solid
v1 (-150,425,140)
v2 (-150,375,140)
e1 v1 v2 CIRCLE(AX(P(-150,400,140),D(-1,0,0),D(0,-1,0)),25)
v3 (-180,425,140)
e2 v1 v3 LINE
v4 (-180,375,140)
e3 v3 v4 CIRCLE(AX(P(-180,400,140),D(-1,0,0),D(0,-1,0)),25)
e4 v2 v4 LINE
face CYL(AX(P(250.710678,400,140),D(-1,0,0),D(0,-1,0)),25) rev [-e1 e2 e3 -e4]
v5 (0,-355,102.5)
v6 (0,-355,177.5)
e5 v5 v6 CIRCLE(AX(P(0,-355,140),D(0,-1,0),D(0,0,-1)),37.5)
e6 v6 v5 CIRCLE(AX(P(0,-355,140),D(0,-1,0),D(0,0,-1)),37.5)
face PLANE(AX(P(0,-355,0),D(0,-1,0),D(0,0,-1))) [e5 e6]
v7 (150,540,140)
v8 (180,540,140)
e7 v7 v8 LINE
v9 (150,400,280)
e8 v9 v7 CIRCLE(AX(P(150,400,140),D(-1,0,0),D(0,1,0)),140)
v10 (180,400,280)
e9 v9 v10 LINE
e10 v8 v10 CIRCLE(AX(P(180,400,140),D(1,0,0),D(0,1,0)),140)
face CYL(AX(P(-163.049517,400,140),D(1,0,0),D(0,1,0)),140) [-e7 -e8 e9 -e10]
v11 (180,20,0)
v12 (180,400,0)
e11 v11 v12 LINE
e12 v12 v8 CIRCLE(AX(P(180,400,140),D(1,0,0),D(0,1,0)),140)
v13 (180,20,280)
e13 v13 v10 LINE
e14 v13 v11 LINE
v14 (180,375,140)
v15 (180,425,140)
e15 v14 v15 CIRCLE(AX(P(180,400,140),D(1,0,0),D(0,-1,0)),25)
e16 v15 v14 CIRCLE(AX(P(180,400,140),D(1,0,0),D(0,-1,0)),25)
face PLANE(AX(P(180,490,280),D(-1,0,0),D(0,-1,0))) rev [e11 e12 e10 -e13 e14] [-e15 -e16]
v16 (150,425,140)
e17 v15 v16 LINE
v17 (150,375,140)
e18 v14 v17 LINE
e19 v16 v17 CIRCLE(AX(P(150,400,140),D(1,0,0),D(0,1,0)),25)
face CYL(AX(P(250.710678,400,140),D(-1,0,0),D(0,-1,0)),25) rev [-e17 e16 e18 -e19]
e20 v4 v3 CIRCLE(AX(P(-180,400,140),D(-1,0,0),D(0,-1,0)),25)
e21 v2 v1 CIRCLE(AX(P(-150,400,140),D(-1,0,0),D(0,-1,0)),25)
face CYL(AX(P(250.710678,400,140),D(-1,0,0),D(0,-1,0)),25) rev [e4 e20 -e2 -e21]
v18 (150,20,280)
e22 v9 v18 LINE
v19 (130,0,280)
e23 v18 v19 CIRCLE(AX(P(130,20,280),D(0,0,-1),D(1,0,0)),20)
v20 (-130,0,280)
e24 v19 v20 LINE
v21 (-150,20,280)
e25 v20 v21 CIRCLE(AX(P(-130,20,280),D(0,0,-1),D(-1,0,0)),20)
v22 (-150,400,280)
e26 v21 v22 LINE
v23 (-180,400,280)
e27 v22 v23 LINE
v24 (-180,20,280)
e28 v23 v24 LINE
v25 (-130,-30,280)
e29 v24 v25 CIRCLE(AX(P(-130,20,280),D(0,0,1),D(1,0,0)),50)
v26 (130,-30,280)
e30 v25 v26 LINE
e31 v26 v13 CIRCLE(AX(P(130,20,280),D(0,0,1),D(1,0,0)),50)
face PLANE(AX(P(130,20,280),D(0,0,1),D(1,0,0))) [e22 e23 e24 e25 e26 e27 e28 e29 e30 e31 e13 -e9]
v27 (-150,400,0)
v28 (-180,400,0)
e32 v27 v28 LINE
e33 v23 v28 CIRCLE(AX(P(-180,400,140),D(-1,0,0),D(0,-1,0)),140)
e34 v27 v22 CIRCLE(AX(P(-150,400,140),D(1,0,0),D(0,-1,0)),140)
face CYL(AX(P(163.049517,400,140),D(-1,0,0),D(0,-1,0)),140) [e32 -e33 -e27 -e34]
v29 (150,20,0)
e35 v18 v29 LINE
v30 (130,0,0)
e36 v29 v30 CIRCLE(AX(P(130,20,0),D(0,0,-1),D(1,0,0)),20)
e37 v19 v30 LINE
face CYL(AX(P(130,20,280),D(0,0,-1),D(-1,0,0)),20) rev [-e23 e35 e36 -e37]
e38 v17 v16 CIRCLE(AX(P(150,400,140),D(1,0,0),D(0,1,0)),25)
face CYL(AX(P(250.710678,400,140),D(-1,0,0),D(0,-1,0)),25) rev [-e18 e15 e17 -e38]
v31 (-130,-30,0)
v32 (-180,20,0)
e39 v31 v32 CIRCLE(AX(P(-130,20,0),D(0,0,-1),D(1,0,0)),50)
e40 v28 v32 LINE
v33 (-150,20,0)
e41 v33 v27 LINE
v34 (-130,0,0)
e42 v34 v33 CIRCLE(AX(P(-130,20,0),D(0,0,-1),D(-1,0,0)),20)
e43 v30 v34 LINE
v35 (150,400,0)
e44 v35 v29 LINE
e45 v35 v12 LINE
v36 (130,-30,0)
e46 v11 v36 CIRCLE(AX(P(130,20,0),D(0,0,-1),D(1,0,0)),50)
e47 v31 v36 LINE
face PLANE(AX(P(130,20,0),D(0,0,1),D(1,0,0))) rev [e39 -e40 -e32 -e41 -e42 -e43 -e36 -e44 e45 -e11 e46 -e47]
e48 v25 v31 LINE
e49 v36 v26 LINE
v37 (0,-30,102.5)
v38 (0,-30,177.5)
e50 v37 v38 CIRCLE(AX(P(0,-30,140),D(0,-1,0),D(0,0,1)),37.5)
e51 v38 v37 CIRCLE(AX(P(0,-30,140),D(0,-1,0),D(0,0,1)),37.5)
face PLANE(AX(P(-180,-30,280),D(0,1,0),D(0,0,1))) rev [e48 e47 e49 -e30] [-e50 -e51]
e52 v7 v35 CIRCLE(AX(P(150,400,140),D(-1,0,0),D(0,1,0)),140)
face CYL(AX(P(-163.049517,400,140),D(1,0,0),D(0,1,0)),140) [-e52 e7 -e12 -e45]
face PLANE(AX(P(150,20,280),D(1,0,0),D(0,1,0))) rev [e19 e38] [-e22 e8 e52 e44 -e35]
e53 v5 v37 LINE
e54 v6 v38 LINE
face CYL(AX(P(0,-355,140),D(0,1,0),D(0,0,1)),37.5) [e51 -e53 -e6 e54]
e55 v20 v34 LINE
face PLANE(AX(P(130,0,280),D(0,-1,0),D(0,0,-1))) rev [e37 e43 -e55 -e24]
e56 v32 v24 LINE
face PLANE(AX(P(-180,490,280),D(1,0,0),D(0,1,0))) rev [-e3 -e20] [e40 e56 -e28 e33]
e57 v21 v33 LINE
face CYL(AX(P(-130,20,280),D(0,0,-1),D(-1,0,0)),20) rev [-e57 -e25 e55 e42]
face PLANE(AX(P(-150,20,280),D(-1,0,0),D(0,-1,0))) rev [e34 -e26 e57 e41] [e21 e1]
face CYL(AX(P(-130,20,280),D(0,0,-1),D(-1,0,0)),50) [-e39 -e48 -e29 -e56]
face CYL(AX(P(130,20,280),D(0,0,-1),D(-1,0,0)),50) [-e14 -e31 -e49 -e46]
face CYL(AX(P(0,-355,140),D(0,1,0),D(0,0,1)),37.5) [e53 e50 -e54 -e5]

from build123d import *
from build123d.topology import SkipClean

# Parameters (mm, degrees)
BOSS_EXTRUDE1_DEPTH = 280
FILLET1_R           = 50
BOSS_EXTRUDE3_START = -30
BOSS_EXTRUDE3_DEPTH = 30
CUT_EXTRUDE5_START  = -30
CUT_EXTRUDE5_DEPTH  = 30
BOSS_EXTRUDE4_DEPTH = 30
CUT_EXTRUDE6_DEPTH  = 30
BOSS_EXTRUDE5_DEPTH = 325
CUT_EXTRUDE7_REACH  = 708.824
SKETCH7_R           = 25


with BuildPart() as part:
    # Sketch1 → Boss-Extrude1 (new body)
    with BuildSketch(Plane.XY):
        with BuildLine():
            Line((130, 0), (-130, 0))
            ThreePointArc((-130, 0), (-144.142135624, 5.857864376), (-150, 20))
            Line((-150, 20), (-150, 490))
            Line((-150, 490), (-180, 490))
            Line((-180, 490), (-180, -30))
            Line((-180, -30), (180, -30))
            Line((180, -30), (180, 490))
            Line((180, 490), (150, 490))
            Line((150, 490), (150, 20))
            ThreePointArc((150, 20), (144.142135624, 5.857864376), (130, 0))
        make_face()
    extrude(amount=BOSS_EXTRUDE1_DEPTH)

    # Fillet1
    fillet1_edges = [part.edges().sort_by_distance(p)[0] for p in [
        (180, -30, 140),
        (-180, -30, 140),
    ]]
    fillet(fillet1_edges, radius=FILLET1_R)

    # Sketch4 → Boss-Extrude3 (add)
    with BuildSketch(Plane.ZY.offset(180).offset(BOSS_EXTRUDE3_START)):
        with BuildLine():
            Line((247.238052948, 490), (140, 490))
            Line((140, 490), (140, 400))
            Line((140, 400), (280, 400))
            ThreePointArc((280, 400), (271.554793551, 447.888790898), (247.238052948, 490))
        make_face()
        with BuildLine():
            Line((140, 400), (140, 490))
            Line((140, 490), (32.761947052, 490))
            ThreePointArc((32.761947052, 490), (8.445206449, 447.888790898), (0, 400))
            Line((0, 400), (140, 400))
        make_face()
        with BuildLine():
            Line((247.238052948, 490), (140, 490))
            Line((140, 490), (140, 400))
            Line((140, 400), (280, 400))
            ThreePointArc((280, 400), (271.554793551, 447.888790898), (247.238052948, 490))
        make_face()
        with BuildLine():
            Line((140, 400), (140, 490))
            Line((140, 490), (32.761947052, 490))
            ThreePointArc((32.761947052, 490), (8.445206449, 447.888790898), (0, 400))
            Line((0, 400), (140, 400))
        make_face()
        with BuildLine():
            Line((32.761947052, 490), (140, 490))
            Line((140, 490), (247.238052948, 490))
            ThreePointArc((247.238052948, 490), (140, 540), (32.761947052, 490))
        make_face()
    extrude(amount=BOSS_EXTRUDE3_DEPTH)

    # Sketch4<3> → Cut-Extrude5 (cut)
    with SkipClean():  # the faces are left unmerged after this step: merging them gives an invalid solid
        with BuildSketch(Plane.ZY.offset(180).offset(CUT_EXTRUDE5_START)):
            with BuildLine():
                Line((0, 490), (0, 400))
                ThreePointArc((0, 400), (8.445206449, 447.888790898), (32.761947052, 490))
                Line((32.761947052, 490), (0, 490))
            make_face()
            with BuildLine():
                ThreePointArc((247.238052948, 490), (271.554793551, 447.888790898), (280, 400))
                Line((280, 400), (280, 490))
                Line((280, 490), (247.238052948, 490))
            make_face()
        extrude(amount=CUT_EXTRUDE5_DEPTH, mode=Mode.SUBTRACT)

    # Sketch5 → Boss-Extrude4 (add)
    with SkipClean():  # the faces are left unmerged after this step: merging them gives an invalid solid
        with BuildSketch(Plane(origin=(180, 0, 0), x_dir=(0, 0, -1), z_dir=(1, 0, 0))):
            with BuildLine():
                Line((-280, 400), (0, 400))
                ThreePointArc((0, 400), (-140, 540), (-280, 400))
            make_face()
        extrude(amount=-BOSS_EXTRUDE4_DEPTH)

    # Sketch5<2> → Cut-Extrude6 (cut)
    with SkipClean():  # the faces are left unmerged after this step: merging them gives an invalid solid
        with BuildSketch(Plane(origin=(180, 0, 0), x_dir=(0, 0, -1), z_dir=(1, 0, 0))):
            with BuildLine():
                Line((-280, 490), (-280, 400))
                ThreePointArc((-280, 400), (-271.554793551, 447.888790898), (-247.238052948, 490))
                Line((-247.238052948, 490), (-280, 490))
            make_face()
            with BuildLine():
                ThreePointArc((-32.761947052, 490), (-8.445206449, 447.888790898), (0, 400))
                Line((0, 400), (0, 490))
                Line((0, 490), (-32.761947052, 490))
            make_face()
        extrude(amount=-CUT_EXTRUDE6_DEPTH, mode=Mode.SUBTRACT)

    # Sketch6 → Boss-Extrude5 (add)
    with SkipClean():  # the faces are left unmerged after this step: merging them gives an invalid solid
        with BuildSketch(Plane.XZ.offset(30)):
            with BuildLine():
                ThreePointArc((37.5, 140), (26.516504294, 166.516504294), (0, 177.5))
                Line((0, 177.5), (0, 102.5))
                ThreePointArc((0, 102.5), (26.516504294, 113.483495706), (37.5, 140))
            make_face()
            with BuildLine():
                Line((0, 102.5), (0, 177.5))
                ThreePointArc((0, 177.5), (-37.5, 140), (0, 102.5))
            make_face()
            with BuildLine():
                ThreePointArc((37.5, 140), (26.516504294, 166.516504294), (0, 177.5))
                Line((0, 177.5), (0, 102.5))
                ThreePointArc((0, 102.5), (26.516504294, 113.483495706), (37.5, 140))
            make_face()
            with BuildLine():
                Line((0, 102.5), (0, 177.5))
                ThreePointArc((0, 177.5), (-37.5, 140), (0, 102.5))
            make_face()
        extrude(amount=BOSS_EXTRUDE5_DEPTH)

    # Cut-Extrude7: up to this face of the body (flat: up to its plane)
    cut_extrude7_end = Plane(part.part.faces().sort_by_distance((180, 210, 140))[0])
    # Sketch7 → Cut-Extrude7 (cut, up to the picked face)
    with BuildSketch(Plane.ZY.offset(180), mode=Mode.PRIVATE) as cut_extrude7_sk1:
        with Locations(Location((140, 400, 0), (0, 0, 270))):
            Circle(SKETCH7_R)
    cut_extrude7_tool1 = split(extrude(cut_extrude7_sk1.sketch, amount=-CUT_EXTRUDE7_REACH, mode=Mode.PRIVATE), bisect_by=cut_extrude7_end, keep=Keep.BOTH, mode=Mode.PRIVATE)
    add(cut_extrude7_tool1.solids().sort_by(Axis((-180, 400, 140), (1, 0, 0)))[0], mode=Mode.SUBTRACT)


solid = part.part
